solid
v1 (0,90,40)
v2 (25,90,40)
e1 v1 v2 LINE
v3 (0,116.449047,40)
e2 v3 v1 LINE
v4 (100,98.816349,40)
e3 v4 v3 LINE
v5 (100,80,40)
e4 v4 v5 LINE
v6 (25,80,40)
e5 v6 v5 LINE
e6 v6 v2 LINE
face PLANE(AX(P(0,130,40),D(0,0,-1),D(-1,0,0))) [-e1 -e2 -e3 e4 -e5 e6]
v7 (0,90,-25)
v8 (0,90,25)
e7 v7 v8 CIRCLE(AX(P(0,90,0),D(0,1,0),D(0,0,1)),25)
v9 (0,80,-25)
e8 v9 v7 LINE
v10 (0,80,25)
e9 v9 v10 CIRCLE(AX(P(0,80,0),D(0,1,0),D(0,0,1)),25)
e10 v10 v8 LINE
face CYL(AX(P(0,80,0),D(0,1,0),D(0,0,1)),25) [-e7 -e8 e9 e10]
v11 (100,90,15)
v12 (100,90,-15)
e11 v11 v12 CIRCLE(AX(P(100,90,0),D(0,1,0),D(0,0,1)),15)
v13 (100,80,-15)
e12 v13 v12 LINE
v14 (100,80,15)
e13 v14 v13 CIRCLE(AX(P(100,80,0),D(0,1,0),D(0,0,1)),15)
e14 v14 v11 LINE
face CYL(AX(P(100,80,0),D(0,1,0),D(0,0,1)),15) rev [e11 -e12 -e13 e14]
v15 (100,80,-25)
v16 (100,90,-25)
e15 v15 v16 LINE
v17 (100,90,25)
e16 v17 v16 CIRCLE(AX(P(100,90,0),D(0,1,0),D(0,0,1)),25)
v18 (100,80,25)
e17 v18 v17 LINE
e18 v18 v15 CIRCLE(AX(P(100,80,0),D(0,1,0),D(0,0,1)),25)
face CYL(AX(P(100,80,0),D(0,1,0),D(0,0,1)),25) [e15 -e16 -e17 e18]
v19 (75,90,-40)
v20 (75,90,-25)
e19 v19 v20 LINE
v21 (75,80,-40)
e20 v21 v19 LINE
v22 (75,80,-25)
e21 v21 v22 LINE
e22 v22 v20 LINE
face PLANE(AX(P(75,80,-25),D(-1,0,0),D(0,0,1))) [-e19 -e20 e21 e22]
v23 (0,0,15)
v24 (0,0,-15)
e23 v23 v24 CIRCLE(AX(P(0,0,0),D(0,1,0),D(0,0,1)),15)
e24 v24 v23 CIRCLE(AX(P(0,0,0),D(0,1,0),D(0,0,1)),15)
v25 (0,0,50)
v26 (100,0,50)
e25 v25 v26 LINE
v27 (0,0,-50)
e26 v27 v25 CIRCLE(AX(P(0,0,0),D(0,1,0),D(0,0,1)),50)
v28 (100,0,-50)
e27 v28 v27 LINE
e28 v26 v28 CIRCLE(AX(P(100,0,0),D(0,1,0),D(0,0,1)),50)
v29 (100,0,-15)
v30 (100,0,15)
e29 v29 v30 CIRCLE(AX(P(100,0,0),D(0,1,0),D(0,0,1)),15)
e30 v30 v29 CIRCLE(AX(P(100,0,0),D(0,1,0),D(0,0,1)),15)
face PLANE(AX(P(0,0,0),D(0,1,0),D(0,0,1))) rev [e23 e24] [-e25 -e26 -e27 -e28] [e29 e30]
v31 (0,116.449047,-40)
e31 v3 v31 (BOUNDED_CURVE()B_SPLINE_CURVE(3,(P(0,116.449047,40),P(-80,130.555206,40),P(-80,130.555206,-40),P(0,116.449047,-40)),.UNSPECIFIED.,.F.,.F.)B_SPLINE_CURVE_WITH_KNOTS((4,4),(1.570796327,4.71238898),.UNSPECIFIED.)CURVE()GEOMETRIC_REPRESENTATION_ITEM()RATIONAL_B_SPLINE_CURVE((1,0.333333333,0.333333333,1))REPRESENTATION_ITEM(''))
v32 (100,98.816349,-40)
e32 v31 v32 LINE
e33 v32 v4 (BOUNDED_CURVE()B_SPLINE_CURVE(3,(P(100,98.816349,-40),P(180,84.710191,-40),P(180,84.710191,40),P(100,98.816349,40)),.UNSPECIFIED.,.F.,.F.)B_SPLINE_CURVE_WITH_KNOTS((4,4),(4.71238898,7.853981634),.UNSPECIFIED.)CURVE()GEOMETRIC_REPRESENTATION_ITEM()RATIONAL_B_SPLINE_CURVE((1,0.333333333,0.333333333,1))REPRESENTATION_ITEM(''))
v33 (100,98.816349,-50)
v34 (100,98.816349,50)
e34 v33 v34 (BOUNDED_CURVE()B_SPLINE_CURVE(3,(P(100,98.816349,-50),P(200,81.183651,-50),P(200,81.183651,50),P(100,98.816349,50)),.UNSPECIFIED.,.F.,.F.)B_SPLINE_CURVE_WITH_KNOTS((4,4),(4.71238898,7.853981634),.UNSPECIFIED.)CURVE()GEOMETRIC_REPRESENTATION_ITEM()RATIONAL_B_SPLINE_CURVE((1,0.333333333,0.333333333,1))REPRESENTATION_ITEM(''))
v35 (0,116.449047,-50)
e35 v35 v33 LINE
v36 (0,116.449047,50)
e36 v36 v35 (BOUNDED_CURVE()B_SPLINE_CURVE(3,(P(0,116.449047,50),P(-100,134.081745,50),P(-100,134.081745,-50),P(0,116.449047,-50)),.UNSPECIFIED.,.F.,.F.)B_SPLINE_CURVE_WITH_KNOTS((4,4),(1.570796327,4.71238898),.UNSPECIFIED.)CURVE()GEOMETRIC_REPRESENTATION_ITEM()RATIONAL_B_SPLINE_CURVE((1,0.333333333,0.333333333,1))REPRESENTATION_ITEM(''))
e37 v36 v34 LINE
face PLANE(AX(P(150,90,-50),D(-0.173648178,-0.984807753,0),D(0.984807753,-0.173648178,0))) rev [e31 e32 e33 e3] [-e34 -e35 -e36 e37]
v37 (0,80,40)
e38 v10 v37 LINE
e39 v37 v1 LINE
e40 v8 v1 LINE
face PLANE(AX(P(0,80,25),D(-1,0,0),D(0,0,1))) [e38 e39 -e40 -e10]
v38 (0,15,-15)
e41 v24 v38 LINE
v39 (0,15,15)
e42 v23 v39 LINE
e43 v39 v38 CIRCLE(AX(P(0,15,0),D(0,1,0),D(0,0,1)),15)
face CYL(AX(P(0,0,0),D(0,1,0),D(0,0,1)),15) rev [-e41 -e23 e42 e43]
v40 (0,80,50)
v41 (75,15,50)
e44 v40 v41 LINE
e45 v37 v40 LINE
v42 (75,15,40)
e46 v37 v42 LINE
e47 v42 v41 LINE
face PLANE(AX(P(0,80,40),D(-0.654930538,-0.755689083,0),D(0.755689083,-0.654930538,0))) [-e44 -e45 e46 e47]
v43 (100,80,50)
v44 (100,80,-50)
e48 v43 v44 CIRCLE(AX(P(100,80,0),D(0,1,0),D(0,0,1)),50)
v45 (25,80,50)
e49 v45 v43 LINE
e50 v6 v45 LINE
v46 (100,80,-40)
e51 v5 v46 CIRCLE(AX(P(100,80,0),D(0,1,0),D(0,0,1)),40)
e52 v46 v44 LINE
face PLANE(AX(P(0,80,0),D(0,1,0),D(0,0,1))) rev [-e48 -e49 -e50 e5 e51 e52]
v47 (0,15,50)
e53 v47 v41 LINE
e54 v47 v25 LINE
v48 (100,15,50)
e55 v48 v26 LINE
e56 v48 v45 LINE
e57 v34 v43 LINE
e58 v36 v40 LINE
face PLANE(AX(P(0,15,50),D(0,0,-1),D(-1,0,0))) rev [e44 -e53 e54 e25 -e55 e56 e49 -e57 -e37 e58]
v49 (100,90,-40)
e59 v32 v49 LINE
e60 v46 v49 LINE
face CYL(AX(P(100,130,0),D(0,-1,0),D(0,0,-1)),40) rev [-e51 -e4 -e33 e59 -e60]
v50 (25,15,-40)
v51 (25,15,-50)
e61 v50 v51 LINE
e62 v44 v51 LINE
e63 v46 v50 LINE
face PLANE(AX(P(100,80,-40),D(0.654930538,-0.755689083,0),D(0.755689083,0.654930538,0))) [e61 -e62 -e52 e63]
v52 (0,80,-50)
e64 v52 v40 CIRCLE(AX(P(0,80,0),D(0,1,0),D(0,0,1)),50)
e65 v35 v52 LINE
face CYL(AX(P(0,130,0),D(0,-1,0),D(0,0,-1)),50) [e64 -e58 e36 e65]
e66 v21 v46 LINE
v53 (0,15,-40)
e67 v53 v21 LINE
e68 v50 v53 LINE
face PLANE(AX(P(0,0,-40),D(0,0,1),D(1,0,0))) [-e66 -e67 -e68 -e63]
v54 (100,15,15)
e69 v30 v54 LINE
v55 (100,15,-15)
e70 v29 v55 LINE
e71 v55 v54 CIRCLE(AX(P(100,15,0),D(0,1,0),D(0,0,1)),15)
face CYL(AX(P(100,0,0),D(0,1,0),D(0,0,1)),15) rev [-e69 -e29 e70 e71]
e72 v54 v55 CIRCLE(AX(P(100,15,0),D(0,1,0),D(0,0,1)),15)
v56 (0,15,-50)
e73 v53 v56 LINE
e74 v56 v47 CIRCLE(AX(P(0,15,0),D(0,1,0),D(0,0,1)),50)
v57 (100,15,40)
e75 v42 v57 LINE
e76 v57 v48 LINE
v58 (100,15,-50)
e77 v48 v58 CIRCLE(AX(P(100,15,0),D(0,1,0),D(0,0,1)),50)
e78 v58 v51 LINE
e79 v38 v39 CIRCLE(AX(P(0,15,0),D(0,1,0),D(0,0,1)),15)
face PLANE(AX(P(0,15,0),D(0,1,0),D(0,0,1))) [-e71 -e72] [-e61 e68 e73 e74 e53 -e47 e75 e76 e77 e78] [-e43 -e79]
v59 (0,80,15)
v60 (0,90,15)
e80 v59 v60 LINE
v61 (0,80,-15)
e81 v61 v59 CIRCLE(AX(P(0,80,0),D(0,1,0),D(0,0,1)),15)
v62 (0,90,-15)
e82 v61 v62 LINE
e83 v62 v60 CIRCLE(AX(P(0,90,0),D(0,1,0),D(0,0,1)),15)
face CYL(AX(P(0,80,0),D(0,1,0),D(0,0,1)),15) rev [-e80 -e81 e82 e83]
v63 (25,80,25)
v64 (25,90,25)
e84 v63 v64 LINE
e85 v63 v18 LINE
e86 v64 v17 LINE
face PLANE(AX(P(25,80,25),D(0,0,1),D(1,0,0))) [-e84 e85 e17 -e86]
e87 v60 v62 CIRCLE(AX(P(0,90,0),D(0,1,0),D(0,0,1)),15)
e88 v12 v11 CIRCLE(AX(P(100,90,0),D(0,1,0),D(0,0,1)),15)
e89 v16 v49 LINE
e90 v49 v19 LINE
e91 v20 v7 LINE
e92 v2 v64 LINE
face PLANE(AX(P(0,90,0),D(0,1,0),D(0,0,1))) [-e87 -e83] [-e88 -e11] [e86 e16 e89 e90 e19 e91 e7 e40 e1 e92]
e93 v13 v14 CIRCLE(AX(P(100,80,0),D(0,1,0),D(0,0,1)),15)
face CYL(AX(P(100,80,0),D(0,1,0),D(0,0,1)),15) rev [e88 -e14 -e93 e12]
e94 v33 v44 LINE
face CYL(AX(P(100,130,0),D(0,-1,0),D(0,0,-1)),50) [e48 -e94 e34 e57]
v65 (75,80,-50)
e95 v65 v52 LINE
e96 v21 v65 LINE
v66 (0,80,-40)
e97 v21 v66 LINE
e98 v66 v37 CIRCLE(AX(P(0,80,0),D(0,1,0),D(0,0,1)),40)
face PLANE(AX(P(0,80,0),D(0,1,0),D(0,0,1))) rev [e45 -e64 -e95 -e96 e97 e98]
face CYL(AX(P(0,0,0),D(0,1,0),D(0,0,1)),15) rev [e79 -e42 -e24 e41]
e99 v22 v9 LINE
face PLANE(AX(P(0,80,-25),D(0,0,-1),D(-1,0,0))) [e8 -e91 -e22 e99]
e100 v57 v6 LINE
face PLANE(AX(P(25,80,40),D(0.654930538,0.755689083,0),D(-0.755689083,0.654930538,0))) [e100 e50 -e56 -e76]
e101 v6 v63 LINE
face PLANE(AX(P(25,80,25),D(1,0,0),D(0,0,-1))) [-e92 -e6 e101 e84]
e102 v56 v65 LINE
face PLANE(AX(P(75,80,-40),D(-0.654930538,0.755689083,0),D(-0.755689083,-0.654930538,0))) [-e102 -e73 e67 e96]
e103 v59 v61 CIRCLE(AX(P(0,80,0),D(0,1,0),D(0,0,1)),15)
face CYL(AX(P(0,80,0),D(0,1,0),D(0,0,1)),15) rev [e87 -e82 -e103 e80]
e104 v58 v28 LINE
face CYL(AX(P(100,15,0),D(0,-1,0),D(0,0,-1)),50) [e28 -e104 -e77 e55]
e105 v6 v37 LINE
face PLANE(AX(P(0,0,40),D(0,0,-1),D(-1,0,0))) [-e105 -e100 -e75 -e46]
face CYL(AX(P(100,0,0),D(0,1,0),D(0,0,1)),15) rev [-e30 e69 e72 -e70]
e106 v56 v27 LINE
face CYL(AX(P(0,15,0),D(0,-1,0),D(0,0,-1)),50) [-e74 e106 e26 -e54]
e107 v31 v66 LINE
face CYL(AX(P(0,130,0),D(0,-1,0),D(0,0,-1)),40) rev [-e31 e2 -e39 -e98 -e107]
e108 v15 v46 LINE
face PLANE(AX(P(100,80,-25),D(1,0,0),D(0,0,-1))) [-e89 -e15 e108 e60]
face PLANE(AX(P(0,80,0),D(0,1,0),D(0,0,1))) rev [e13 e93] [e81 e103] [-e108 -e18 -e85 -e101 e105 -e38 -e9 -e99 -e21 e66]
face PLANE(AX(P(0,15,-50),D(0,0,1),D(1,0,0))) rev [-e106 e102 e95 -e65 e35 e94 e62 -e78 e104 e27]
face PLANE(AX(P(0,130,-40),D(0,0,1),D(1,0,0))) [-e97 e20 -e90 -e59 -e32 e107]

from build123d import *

# Parameters (mm, degrees)
BASE_PLATE_DEPTH            = 15
BASE_BORE_SKETCH_R          = 15
BASE_BORE_DEPTH             = 15
LOOP_START                  = -10
LOOP_RING_DEPTH             = 50
BRACE_ANGLE_CUT_DEPTH       = 223.261107709
X_BRACE_WEB_DEPTH           = 10
BRACE_TRIM_CUT_SKETCH_R     = 15
BRACE_TRIM_CUT_DEPTH        = 10
INNER_PLATE_DEPTH           = 10
INNER_PLATE_EXTENSION_DEPTH = 10


with BuildPart() as part:
    # Base Plate Sketch → Base Plate (new body)
    with BuildSketch(Plane(origin=(0, 0, 0), x_dir=(1, 0, 0), z_dir=(0, 1, 0))):
        with BuildLine():
            Line((0, 50), (100, 50))
            ThreePointArc((100, 50), (150, 0), (100, -50))
            Line((100, -50), (0, -50))
            ThreePointArc((0, -50), (-50, 0), (0, 50))
        make_face()
    extrude(amount=BASE_PLATE_DEPTH)

    # Base Bore Sketch → Base Bore (cut)
    with BuildSketch(Plane(origin=(0, 15, 0), x_dir=(1, 0, 0), z_dir=(0, 1, 0))):
        with Locations(Location((100, 0, 0), (0, 0, 270))):
            Circle(BASE_BORE_SKETCH_R)
        with Locations(Location((0, 0, 0), (0, 0, 270))):
            Circle(BASE_BORE_SKETCH_R)
    extrude(amount=-BASE_BORE_DEPTH, mode=Mode.SUBTRACT)



with BuildPart() as body_2:
    # Loop Ring Sketch → Loop Ring (new body)
    with BuildSketch(Plane(origin=(0, 90, 0), x_dir=(1, 0, 0), z_dir=(0, 1, 0)).offset(LOOP_START)):
        with BuildLine():
            Line((0, -50), (100, -50))
            ThreePointArc((100, -50), (150, 0), (100, 50))
            Line((100, 50), (0, 50))
            ThreePointArc((0, 50), (-50, 0), (0, -50))
        make_face()
        with BuildLine():
            Line((0, 40), (100, 40))
            ThreePointArc((100, 40), (140, 0), (100, -40))
            Line((100, -40), (0, -40))
            ThreePointArc((0, -40), (-40, 0), (0, 40))
        make_face(mode=Mode.SUBTRACT)
    extrude(amount=LOOP_RING_DEPTH)

    # Brace Angle Cut Sketch → Brace Angle Cut (cut, through all)
    with BuildSketch(Plane.XY.offset(50)):
        Polygon((150, 90), (150, 130), (-50, 130), (-50, 125.265396142), align=None)
    extrude(amount=-BRACE_ANGLE_CUT_DEPTH, mode=Mode.SUBTRACT)

    # X-Brace Sketch → X-Brace Web (add)
    with BuildSketch(Plane(origin=(0, 90, 0), x_dir=(1, 0, 0), z_dir=(0, 1, 0))):
        with BuildLine():
            Line((0, 25), (75, 25))
            Line((75, 25), (75, 40))
            Line((75, 40), (100, 40))
            Line((100, 40), (100, 25))
            ThreePointArc((100, 25), (125, 0), (100, -25))
            Line((100, -25), (25, -25))
            Line((25, -25), (25, -40))
            Line((25, -40), (0, -40))
            Line((0, -40), (0, -25))
            ThreePointArc((0, -25), (-25, 0), (0, 25))
        make_face()
    extrude(amount=-X_BRACE_WEB_DEPTH)

    # Brace Trim Cut Sketch → Brace Trim Cut (cut)
    with BuildSketch(Plane(origin=(0, 90, 0), x_dir=(1, 0, 0), z_dir=(0, 1, 0))):
        with Locations(Location((100, 0, 0), (0, 0, 270))):
            Circle(BRACE_TRIM_CUT_SKETCH_R)
        with Locations(Location((0, 0, 0), (0, 0, 270))):
            Circle(BRACE_TRIM_CUT_SKETCH_R)
    extrude(amount=-BRACE_TRIM_CUT_DEPTH, mode=Mode.SUBTRACT)


with BuildPart() as part_1:
    add(part.part)

    add(body_2.part)  # Inner Plate merges body 2
    # Inner Plate Sketch → Inner Plate (add)
    with BuildSketch(Plane.XY.offset(50)):
        Polygon((0, 80), (75, 15), (100, 15), (25, 80), align=None)
    extrude(amount=-INNER_PLATE_DEPTH)

    # Inner Plate Extension Sketch → Inner Plate Extension (add)
    with BuildSketch(Plane(origin=(0, 0, -50), x_dir=(-1, 0, 0), z_dir=(0, 0, -1))):
        Polygon((-100, 80), (-25, 15), (0, 15), (-75, 80), align=None)
    extrude(amount=-INNER_PLATE_EXTENSION_DEPTH)


solid = part_1.part
